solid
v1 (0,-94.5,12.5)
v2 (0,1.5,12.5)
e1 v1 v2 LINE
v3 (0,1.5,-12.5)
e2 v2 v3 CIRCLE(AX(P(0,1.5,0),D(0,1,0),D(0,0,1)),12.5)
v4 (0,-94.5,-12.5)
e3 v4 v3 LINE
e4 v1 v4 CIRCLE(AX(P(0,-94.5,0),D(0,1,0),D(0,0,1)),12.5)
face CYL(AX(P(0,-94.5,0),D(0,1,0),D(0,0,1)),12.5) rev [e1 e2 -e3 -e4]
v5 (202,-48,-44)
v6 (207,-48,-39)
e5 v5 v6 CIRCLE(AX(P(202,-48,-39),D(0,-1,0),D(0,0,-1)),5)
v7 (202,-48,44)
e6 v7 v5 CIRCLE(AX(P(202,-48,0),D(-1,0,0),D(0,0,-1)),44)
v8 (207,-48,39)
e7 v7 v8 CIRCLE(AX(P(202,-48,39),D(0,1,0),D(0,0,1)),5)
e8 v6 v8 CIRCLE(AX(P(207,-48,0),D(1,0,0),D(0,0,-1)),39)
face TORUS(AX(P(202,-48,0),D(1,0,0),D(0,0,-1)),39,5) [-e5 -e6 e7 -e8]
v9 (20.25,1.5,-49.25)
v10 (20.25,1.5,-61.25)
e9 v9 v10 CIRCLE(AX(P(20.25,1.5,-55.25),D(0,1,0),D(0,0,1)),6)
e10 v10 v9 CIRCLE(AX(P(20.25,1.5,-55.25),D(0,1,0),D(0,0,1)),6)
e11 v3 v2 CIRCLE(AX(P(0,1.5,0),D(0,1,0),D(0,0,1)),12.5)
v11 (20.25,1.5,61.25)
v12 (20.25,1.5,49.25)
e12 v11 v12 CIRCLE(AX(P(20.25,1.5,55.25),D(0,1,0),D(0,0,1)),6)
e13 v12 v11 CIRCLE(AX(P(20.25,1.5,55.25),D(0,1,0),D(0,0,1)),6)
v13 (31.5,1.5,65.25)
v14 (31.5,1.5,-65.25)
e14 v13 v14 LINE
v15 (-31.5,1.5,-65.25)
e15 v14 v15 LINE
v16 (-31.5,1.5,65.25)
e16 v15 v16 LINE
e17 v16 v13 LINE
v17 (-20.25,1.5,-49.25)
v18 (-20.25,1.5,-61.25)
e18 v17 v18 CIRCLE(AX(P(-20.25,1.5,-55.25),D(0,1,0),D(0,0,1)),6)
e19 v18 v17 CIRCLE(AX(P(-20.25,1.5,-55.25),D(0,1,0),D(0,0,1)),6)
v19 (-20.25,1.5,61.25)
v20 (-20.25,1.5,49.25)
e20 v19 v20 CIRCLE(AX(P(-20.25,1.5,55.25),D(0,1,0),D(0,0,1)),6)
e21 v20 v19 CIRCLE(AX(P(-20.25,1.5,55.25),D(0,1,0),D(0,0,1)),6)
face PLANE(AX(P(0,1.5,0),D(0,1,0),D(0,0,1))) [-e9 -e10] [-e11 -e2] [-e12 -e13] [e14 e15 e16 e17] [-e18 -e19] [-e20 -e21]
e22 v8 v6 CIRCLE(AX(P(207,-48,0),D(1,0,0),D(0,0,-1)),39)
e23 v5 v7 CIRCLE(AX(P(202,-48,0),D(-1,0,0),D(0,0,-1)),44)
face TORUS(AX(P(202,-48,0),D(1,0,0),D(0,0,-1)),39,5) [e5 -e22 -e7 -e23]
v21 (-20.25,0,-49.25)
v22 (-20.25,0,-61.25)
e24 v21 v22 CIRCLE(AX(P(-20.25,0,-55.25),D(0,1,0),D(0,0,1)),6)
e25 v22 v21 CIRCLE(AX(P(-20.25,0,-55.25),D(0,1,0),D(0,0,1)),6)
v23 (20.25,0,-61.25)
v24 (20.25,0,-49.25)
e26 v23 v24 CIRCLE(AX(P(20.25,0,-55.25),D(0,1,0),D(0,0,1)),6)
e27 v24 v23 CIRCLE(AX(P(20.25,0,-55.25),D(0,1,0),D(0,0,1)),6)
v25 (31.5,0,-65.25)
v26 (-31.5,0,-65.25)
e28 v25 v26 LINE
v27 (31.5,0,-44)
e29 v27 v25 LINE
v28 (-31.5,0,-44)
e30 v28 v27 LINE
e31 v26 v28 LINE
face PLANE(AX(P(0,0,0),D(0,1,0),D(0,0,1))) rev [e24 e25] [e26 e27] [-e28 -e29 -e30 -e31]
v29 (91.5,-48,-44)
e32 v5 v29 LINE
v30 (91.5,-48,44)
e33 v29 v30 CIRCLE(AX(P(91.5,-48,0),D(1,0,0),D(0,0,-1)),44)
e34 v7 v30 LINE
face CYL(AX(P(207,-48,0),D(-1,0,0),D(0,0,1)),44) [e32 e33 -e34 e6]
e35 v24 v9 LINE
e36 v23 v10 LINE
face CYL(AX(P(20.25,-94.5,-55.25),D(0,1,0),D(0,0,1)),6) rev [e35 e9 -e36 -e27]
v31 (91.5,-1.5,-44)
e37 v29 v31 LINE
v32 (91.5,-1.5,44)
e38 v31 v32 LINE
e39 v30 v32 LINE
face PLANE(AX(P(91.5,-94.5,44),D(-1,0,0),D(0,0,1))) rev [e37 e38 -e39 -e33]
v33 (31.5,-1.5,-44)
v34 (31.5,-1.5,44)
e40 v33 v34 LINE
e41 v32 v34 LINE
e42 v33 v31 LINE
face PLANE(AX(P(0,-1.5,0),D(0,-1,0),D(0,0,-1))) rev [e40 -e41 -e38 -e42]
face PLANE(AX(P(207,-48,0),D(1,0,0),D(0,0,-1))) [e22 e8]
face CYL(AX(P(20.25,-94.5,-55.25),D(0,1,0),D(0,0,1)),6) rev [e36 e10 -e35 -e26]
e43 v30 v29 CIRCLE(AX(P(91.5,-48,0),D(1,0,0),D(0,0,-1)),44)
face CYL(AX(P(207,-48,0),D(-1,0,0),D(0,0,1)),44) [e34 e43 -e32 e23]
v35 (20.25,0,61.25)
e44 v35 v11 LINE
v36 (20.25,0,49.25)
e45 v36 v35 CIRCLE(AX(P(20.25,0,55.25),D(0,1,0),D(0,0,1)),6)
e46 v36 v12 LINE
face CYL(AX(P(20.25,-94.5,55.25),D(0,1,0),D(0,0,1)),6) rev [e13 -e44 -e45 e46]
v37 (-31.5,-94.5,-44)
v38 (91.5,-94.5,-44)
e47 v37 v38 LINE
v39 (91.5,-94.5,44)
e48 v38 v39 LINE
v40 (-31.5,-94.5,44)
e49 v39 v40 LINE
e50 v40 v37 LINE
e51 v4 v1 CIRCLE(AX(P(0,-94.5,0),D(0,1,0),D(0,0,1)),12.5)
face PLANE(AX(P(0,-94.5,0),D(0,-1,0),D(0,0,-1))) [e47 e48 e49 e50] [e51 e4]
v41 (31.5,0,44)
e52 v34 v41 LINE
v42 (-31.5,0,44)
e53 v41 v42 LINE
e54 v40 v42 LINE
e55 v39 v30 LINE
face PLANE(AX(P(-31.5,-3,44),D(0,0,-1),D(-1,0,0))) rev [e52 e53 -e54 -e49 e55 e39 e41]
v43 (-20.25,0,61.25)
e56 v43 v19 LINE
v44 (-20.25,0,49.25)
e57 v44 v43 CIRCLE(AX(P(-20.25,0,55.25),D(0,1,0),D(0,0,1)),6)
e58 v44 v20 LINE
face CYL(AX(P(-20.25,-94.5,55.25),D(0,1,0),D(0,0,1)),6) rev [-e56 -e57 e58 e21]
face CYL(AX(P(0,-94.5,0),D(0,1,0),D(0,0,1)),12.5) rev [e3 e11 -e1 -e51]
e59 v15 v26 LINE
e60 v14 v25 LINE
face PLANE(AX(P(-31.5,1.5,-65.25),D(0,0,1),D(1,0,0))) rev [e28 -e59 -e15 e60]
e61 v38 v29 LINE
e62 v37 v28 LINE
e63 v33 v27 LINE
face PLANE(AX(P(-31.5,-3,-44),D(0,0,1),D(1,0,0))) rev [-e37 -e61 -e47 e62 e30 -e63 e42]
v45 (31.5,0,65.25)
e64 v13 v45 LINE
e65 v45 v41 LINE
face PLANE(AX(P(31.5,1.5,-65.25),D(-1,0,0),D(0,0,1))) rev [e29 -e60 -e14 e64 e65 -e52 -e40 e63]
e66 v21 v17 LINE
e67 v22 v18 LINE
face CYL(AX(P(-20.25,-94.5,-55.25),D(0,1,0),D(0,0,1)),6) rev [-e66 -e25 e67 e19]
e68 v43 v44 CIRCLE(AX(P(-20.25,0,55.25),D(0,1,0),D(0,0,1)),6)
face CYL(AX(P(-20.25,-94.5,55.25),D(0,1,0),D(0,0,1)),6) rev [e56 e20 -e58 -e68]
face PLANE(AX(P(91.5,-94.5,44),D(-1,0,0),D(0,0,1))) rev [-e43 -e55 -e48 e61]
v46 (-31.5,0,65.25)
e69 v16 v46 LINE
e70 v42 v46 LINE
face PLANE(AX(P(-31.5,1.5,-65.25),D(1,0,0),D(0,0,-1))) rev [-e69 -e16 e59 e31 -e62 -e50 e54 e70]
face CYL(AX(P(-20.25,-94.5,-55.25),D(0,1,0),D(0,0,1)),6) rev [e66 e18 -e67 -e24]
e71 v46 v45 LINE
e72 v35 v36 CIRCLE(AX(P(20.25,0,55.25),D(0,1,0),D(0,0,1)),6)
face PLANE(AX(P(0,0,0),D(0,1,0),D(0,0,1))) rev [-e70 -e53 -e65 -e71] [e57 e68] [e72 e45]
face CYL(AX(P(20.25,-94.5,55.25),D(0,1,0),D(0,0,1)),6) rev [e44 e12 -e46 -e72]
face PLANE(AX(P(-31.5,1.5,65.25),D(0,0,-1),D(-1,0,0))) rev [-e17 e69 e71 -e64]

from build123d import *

# Parameters (mm, degrees)
SKETCH_1_W          = 63
SKETCH_1_H          = 130.5
EXTRUDE_1_DEPTH     = 1.5
EXTRUDE_START       = 1.5
SKETCH_2_W          = 123
SKETCH_2_H          = 88
EXTRUDE_2_DEPTH     = 93
SKETCH_3_R          = 44
EXTRUDE_3_DEPTH     = 115.5
SKETCH_5_W          = 63
SKETCH_5_H          = 88
EXTRUDE_4_DEPTH     = 3
SKETCH_6_R          = 6
CUT_EXTRUDE_2_DEPTH = 238.323750392
SKETCH_4_R          = 12.5
CUT_EXTRUDE_1_DEPTH = 238.323750392
FILLET_1_R          = 5


with BuildPart() as part:
    # 草图1 → 凸台-拉伸1 (new body)
    with BuildSketch(Plane(origin=(0, 0, 0), x_dir=(1, 0, 0), z_dir=(0, 1, 0))):
        Rectangle(SKETCH_1_W, SKETCH_1_H)
    extrude(amount=EXTRUDE_1_DEPTH)



with BuildPart() as body_2:
    # 草图2 → 凸台-拉伸2 (new body)
    with BuildSketch(Plane.XZ.offset(EXTRUDE_START)):
        with Locations((30, 0)):
            Rectangle(SKETCH_2_W, SKETCH_2_H)
    extrude(amount=EXTRUDE_2_DEPTH)

    # 草图3 → 凸台-拉伸3 (add)
    with BuildSketch(Plane(origin=(91.5, 0, 0), x_dir=(0, 0, -1), z_dir=(1, 0, 0))):
        with Locations((0, -48)):
            Circle(SKETCH_3_R)
    extrude(amount=EXTRUDE_3_DEPTH)


with BuildPart() as part_1:
    add(part.part)

    add(body_2.part)  # 凸台-拉伸4 merges body 2
    # 草图5 → 凸台-拉伸4 (add)
    with BuildSketch(Plane.XZ):
        Rectangle(SKETCH_5_W, SKETCH_5_H)
    extrude(amount=EXTRUDE_4_DEPTH)

    # 草图6 → 切除-拉伸2 (cut, through all)
    with BuildSketch(Plane(origin=(0, 1.5, 0), x_dir=(1, 0, 0), z_dir=(0, 1, 0))):
        with Locations(Location((-20.25, 55.25, 0), (0, 0, 270))):
            Circle(SKETCH_6_R)
        with Locations(Location((20.25, 55.25, 0), (0, 0, 270))):
            Circle(SKETCH_6_R)
        with Locations(Location((-20.25, -55.25, 0), (0, 0, 270))):
            Circle(SKETCH_6_R)
        with Locations(Location((20.25, -55.25, 0), (0, 0, 270))):
            Circle(SKETCH_6_R)
    extrude(amount=-CUT_EXTRUDE_2_DEPTH, mode=Mode.SUBTRACT)

    # 草图4 → 切除-拉伸1 (cut, through all)
    with BuildSketch(Plane(origin=(0, 1.5, 0), x_dir=(1, 0, 0), z_dir=(0, 1, 0))):
        with Locations(Location((0, 0, 0), (0, 0, 270))):
            Circle(SKETCH_4_R)
    extrude(amount=-CUT_EXTRUDE_1_DEPTH, mode=Mode.SUBTRACT)

    # 圆角1
    fillet_1_edges = [part_1.edges().sort_by_distance(p)[0] for p in [
        (207, -48, 44),
    ]]
    fillet(fillet_1_edges, radius=FILLET_1_R)


solid = part_1.part
